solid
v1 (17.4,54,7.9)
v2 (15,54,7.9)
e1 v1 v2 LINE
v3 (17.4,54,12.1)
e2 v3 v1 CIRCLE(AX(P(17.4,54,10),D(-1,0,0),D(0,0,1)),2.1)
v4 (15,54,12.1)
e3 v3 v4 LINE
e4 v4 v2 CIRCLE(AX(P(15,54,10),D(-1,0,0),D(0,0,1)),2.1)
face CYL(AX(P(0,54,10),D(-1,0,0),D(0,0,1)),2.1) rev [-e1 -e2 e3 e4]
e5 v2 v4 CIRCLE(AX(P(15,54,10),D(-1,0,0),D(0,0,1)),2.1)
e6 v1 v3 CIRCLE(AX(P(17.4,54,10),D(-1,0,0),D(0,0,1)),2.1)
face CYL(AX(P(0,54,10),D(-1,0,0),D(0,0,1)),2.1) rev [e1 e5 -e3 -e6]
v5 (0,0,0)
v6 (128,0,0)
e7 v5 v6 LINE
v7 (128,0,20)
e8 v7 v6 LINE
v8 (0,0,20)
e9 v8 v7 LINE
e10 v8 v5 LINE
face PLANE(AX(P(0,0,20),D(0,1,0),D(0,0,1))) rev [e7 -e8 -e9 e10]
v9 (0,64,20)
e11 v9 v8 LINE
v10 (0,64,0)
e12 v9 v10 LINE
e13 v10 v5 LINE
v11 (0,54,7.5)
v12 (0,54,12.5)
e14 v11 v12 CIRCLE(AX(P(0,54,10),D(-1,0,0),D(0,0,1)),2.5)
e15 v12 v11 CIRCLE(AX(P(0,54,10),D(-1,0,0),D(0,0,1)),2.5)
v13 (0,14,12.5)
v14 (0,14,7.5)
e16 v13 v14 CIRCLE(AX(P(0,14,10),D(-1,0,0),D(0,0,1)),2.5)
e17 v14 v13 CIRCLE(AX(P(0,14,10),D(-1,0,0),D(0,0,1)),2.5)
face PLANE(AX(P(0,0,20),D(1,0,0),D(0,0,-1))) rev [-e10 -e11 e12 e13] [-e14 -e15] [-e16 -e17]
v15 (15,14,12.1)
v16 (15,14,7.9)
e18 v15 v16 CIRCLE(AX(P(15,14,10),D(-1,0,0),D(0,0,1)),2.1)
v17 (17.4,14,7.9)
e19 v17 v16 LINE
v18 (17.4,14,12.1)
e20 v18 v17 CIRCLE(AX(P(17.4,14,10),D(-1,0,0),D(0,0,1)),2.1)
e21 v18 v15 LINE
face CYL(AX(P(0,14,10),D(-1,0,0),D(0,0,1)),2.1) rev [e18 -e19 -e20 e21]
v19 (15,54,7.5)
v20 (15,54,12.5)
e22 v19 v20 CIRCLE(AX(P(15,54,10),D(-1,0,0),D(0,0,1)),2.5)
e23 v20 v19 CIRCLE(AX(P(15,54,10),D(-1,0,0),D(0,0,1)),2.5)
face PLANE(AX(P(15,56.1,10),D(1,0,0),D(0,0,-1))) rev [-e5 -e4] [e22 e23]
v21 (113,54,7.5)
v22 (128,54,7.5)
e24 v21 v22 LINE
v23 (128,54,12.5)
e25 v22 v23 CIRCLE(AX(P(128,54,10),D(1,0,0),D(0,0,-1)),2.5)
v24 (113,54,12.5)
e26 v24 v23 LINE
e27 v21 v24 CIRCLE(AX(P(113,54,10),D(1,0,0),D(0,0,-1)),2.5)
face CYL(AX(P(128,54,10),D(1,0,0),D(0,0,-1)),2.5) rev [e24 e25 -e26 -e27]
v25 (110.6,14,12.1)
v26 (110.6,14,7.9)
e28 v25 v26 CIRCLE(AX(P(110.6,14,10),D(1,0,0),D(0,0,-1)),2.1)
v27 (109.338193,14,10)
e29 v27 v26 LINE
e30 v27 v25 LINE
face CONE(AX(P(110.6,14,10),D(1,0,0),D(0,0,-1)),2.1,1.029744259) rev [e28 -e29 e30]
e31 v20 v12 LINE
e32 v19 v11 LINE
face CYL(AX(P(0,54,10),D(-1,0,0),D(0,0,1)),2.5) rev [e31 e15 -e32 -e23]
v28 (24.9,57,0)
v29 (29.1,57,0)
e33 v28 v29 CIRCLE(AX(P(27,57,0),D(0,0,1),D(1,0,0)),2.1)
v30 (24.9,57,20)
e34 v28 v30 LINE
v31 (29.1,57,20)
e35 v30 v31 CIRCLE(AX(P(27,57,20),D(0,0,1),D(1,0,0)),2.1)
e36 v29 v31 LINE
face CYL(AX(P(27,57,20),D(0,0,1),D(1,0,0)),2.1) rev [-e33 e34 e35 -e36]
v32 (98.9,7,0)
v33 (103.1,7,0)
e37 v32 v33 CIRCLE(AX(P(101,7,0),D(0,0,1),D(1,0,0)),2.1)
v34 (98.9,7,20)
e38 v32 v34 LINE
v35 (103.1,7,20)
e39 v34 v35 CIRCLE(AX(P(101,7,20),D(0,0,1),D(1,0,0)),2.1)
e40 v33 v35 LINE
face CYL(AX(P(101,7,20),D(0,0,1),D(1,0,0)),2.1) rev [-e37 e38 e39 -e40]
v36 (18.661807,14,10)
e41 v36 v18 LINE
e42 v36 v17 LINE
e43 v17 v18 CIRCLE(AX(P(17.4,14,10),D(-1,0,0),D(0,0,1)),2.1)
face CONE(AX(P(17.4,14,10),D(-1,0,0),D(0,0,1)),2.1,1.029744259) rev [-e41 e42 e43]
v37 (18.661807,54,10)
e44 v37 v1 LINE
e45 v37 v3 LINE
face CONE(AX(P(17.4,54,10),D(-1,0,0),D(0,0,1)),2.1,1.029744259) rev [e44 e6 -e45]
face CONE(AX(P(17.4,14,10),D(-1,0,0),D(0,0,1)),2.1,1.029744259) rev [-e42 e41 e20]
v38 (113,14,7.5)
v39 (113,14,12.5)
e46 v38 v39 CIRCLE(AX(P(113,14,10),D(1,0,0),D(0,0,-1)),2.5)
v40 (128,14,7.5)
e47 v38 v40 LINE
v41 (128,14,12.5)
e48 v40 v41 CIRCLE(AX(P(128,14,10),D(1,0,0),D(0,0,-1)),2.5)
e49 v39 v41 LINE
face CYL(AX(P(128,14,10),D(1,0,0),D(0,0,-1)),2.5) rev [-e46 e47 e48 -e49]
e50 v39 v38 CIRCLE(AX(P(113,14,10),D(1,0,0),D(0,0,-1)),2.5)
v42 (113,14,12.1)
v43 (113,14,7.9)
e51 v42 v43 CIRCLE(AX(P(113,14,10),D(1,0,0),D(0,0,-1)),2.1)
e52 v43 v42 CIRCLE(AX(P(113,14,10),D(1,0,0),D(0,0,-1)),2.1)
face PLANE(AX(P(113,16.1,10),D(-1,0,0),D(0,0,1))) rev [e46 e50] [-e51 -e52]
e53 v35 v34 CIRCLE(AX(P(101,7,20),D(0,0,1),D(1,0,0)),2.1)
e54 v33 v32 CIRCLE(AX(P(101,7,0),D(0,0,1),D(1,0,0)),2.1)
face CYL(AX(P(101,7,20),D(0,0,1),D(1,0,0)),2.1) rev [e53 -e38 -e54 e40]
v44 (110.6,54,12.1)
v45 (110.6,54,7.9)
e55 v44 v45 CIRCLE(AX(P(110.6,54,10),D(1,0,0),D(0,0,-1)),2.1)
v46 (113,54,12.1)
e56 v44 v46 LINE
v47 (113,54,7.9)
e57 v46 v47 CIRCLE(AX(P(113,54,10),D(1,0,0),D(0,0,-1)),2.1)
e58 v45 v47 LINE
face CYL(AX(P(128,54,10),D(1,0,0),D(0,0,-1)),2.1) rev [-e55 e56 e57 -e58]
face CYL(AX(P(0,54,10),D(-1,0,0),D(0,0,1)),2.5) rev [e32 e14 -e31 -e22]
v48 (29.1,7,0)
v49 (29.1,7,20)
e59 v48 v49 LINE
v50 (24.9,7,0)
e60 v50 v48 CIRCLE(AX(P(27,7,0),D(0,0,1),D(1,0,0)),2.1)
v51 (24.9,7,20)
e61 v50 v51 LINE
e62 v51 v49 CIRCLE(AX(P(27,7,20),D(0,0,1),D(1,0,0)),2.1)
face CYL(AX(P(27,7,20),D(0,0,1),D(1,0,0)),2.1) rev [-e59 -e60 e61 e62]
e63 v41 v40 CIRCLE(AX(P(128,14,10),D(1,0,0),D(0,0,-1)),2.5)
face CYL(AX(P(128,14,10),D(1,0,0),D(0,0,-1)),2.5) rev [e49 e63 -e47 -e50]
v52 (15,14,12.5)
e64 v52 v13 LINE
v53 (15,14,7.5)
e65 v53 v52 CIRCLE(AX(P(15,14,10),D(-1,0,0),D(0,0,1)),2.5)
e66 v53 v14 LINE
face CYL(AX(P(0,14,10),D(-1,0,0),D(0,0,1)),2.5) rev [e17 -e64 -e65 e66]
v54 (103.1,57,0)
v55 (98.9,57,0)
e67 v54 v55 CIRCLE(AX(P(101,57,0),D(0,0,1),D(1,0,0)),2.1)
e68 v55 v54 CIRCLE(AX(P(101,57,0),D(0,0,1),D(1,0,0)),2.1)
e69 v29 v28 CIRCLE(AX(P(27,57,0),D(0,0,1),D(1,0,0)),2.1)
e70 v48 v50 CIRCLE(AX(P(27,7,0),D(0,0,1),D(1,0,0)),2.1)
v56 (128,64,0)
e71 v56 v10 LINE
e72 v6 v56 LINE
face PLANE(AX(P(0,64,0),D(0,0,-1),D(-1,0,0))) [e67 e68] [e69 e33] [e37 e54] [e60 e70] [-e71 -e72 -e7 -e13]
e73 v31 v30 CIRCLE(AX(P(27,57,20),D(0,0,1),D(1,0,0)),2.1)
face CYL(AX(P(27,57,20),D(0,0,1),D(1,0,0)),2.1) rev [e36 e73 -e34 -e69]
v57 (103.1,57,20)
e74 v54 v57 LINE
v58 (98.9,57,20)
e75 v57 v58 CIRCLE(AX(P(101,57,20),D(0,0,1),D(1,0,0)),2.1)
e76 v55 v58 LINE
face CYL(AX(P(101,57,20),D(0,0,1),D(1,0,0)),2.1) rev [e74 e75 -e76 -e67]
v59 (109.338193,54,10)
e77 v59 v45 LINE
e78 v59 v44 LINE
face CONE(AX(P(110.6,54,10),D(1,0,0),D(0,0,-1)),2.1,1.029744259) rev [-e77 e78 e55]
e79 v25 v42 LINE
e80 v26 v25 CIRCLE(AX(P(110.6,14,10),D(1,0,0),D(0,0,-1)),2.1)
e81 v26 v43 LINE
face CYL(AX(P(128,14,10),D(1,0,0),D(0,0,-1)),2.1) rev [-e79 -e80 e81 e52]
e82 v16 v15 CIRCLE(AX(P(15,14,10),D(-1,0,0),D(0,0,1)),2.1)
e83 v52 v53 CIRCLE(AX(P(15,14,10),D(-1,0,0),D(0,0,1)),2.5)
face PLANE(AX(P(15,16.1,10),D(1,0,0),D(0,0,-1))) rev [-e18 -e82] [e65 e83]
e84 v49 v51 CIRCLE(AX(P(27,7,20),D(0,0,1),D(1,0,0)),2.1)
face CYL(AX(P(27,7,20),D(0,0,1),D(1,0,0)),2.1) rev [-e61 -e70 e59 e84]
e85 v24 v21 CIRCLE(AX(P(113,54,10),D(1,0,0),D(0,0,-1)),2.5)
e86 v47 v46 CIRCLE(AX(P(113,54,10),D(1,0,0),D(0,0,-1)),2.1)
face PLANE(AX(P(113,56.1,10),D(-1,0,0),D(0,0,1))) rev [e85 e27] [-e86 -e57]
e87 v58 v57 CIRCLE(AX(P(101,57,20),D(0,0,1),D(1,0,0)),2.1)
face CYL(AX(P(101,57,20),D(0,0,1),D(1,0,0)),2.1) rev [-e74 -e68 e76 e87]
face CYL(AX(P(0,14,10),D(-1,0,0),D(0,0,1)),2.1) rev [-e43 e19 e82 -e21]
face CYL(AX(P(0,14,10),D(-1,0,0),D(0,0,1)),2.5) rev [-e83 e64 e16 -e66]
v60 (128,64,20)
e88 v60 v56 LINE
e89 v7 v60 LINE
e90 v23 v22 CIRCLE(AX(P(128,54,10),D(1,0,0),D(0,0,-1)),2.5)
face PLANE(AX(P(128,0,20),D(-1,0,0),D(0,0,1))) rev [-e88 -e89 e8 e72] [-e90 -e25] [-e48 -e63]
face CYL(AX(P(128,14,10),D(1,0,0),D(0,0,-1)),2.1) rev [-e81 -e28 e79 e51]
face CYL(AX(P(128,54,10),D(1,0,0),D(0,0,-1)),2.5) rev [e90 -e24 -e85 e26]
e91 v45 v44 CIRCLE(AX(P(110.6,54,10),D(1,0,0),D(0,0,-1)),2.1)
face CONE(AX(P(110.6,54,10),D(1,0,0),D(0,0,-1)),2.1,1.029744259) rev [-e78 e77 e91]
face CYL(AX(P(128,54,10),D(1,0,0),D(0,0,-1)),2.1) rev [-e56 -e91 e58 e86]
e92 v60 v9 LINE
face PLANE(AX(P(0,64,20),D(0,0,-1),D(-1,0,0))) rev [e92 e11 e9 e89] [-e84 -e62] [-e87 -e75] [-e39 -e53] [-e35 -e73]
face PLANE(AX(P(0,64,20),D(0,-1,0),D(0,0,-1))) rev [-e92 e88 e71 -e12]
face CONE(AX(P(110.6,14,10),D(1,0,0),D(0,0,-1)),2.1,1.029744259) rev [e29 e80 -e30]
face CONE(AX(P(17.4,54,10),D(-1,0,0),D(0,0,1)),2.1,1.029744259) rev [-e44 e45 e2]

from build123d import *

# Parameters (mm, degrees)
SKETCH_1_W             = 128
SKETCH_1_H             = 64
EXTRUDE_1_DEPTH        = 20
HOLE_WIZARD_M5_1_D     = 4.2
PATTERN_LINEAR_1_COUNT = 2
PATTERN_LINEAR_1_PITCH = 40


with BuildPart() as part:
    # 草图1 → 拉伸1 (new body)
    with BuildSketch(Plane.XY):
        with Locations((64, 32)):
            Rectangle(SKETCH_1_W, SKETCH_1_H)
    extrude(amount=EXTRUDE_1_DEPTH)

    # M5 螺纹孔1 (through all)
    with Locations(Plane.XY.offset(20)):
        with Locations((27, 57), (27, 7), (101, 7), (101, 57)):
            Hole(HOLE_WIZARD_M5_1_D / 2)

    # 草图4 → M5x0.8 螺纹孔1 (revolve, cut)
    with BuildSketch(Plane(origin=(0, 54, 10), x_dir=(0, 0, 1), z_dir=(0, 1, 0))):
        Polygon((0, 0), (0, 18.6618073), (2.1, 17.4), (2.1, 15), (2.5, 15), (2.5, 0), align=None)
    m5x0_8_1 = revolve(axis=Axis((-6.35, 54, 10), (1, 0, 0)), mode=Mode.SUBTRACT)

    # 镜向1: M5x0.8 螺纹孔1 across plane
    add(m5x0_8_1.mirror(Plane(origin=(64, 0, 0), x_dir=(0, 0, 1), z_dir=(1, 0, 0))), mode=Mode.SUBTRACT)

    # 阵列(线性)1: M5x0.8 螺纹孔1 ×2
    with Locations(*[(0, -i * PATTERN_LINEAR_1_PITCH, 0) for i in range(1, PATTERN_LINEAR_1_COUNT)]):
        add(m5x0_8_1, mode=Mode.SUBTRACT)

    # 镜向2 copy 1 sketch → 镜向2 copy 1 (revolve, cut)
    with BuildSketch(Plane(origin=(128, 14, 10), x_dir=(0, 0, 1), z_dir=(0, 1, 0))):
        Polygon((0, 0), (0, -18.6618073), (2.1, -17.4), (2.1, -15), (2.5, -15), (2.5, 0), align=None)
    revolve(axis=Axis((134.35, 14, 10), (1, 0, 0)), mode=Mode.SUBTRACT)

    # 镜向2 copy 2 sketch → 镜向2 copy 2 (revolve, cut)
    with BuildSketch(Plane(origin=(128, 54, 10), x_dir=(0, 0, 1), z_dir=(0, 1, 0))):
        Polygon((0, 0), (0, -18.6618073), (2.1, -17.4), (2.1, -15), (2.5, -15), (2.5, 0), align=None)
    revolve(axis=Axis((134.35, 54, 10), (1, 0, 0)), mode=Mode.SUBTRACT)


solid = part.part
